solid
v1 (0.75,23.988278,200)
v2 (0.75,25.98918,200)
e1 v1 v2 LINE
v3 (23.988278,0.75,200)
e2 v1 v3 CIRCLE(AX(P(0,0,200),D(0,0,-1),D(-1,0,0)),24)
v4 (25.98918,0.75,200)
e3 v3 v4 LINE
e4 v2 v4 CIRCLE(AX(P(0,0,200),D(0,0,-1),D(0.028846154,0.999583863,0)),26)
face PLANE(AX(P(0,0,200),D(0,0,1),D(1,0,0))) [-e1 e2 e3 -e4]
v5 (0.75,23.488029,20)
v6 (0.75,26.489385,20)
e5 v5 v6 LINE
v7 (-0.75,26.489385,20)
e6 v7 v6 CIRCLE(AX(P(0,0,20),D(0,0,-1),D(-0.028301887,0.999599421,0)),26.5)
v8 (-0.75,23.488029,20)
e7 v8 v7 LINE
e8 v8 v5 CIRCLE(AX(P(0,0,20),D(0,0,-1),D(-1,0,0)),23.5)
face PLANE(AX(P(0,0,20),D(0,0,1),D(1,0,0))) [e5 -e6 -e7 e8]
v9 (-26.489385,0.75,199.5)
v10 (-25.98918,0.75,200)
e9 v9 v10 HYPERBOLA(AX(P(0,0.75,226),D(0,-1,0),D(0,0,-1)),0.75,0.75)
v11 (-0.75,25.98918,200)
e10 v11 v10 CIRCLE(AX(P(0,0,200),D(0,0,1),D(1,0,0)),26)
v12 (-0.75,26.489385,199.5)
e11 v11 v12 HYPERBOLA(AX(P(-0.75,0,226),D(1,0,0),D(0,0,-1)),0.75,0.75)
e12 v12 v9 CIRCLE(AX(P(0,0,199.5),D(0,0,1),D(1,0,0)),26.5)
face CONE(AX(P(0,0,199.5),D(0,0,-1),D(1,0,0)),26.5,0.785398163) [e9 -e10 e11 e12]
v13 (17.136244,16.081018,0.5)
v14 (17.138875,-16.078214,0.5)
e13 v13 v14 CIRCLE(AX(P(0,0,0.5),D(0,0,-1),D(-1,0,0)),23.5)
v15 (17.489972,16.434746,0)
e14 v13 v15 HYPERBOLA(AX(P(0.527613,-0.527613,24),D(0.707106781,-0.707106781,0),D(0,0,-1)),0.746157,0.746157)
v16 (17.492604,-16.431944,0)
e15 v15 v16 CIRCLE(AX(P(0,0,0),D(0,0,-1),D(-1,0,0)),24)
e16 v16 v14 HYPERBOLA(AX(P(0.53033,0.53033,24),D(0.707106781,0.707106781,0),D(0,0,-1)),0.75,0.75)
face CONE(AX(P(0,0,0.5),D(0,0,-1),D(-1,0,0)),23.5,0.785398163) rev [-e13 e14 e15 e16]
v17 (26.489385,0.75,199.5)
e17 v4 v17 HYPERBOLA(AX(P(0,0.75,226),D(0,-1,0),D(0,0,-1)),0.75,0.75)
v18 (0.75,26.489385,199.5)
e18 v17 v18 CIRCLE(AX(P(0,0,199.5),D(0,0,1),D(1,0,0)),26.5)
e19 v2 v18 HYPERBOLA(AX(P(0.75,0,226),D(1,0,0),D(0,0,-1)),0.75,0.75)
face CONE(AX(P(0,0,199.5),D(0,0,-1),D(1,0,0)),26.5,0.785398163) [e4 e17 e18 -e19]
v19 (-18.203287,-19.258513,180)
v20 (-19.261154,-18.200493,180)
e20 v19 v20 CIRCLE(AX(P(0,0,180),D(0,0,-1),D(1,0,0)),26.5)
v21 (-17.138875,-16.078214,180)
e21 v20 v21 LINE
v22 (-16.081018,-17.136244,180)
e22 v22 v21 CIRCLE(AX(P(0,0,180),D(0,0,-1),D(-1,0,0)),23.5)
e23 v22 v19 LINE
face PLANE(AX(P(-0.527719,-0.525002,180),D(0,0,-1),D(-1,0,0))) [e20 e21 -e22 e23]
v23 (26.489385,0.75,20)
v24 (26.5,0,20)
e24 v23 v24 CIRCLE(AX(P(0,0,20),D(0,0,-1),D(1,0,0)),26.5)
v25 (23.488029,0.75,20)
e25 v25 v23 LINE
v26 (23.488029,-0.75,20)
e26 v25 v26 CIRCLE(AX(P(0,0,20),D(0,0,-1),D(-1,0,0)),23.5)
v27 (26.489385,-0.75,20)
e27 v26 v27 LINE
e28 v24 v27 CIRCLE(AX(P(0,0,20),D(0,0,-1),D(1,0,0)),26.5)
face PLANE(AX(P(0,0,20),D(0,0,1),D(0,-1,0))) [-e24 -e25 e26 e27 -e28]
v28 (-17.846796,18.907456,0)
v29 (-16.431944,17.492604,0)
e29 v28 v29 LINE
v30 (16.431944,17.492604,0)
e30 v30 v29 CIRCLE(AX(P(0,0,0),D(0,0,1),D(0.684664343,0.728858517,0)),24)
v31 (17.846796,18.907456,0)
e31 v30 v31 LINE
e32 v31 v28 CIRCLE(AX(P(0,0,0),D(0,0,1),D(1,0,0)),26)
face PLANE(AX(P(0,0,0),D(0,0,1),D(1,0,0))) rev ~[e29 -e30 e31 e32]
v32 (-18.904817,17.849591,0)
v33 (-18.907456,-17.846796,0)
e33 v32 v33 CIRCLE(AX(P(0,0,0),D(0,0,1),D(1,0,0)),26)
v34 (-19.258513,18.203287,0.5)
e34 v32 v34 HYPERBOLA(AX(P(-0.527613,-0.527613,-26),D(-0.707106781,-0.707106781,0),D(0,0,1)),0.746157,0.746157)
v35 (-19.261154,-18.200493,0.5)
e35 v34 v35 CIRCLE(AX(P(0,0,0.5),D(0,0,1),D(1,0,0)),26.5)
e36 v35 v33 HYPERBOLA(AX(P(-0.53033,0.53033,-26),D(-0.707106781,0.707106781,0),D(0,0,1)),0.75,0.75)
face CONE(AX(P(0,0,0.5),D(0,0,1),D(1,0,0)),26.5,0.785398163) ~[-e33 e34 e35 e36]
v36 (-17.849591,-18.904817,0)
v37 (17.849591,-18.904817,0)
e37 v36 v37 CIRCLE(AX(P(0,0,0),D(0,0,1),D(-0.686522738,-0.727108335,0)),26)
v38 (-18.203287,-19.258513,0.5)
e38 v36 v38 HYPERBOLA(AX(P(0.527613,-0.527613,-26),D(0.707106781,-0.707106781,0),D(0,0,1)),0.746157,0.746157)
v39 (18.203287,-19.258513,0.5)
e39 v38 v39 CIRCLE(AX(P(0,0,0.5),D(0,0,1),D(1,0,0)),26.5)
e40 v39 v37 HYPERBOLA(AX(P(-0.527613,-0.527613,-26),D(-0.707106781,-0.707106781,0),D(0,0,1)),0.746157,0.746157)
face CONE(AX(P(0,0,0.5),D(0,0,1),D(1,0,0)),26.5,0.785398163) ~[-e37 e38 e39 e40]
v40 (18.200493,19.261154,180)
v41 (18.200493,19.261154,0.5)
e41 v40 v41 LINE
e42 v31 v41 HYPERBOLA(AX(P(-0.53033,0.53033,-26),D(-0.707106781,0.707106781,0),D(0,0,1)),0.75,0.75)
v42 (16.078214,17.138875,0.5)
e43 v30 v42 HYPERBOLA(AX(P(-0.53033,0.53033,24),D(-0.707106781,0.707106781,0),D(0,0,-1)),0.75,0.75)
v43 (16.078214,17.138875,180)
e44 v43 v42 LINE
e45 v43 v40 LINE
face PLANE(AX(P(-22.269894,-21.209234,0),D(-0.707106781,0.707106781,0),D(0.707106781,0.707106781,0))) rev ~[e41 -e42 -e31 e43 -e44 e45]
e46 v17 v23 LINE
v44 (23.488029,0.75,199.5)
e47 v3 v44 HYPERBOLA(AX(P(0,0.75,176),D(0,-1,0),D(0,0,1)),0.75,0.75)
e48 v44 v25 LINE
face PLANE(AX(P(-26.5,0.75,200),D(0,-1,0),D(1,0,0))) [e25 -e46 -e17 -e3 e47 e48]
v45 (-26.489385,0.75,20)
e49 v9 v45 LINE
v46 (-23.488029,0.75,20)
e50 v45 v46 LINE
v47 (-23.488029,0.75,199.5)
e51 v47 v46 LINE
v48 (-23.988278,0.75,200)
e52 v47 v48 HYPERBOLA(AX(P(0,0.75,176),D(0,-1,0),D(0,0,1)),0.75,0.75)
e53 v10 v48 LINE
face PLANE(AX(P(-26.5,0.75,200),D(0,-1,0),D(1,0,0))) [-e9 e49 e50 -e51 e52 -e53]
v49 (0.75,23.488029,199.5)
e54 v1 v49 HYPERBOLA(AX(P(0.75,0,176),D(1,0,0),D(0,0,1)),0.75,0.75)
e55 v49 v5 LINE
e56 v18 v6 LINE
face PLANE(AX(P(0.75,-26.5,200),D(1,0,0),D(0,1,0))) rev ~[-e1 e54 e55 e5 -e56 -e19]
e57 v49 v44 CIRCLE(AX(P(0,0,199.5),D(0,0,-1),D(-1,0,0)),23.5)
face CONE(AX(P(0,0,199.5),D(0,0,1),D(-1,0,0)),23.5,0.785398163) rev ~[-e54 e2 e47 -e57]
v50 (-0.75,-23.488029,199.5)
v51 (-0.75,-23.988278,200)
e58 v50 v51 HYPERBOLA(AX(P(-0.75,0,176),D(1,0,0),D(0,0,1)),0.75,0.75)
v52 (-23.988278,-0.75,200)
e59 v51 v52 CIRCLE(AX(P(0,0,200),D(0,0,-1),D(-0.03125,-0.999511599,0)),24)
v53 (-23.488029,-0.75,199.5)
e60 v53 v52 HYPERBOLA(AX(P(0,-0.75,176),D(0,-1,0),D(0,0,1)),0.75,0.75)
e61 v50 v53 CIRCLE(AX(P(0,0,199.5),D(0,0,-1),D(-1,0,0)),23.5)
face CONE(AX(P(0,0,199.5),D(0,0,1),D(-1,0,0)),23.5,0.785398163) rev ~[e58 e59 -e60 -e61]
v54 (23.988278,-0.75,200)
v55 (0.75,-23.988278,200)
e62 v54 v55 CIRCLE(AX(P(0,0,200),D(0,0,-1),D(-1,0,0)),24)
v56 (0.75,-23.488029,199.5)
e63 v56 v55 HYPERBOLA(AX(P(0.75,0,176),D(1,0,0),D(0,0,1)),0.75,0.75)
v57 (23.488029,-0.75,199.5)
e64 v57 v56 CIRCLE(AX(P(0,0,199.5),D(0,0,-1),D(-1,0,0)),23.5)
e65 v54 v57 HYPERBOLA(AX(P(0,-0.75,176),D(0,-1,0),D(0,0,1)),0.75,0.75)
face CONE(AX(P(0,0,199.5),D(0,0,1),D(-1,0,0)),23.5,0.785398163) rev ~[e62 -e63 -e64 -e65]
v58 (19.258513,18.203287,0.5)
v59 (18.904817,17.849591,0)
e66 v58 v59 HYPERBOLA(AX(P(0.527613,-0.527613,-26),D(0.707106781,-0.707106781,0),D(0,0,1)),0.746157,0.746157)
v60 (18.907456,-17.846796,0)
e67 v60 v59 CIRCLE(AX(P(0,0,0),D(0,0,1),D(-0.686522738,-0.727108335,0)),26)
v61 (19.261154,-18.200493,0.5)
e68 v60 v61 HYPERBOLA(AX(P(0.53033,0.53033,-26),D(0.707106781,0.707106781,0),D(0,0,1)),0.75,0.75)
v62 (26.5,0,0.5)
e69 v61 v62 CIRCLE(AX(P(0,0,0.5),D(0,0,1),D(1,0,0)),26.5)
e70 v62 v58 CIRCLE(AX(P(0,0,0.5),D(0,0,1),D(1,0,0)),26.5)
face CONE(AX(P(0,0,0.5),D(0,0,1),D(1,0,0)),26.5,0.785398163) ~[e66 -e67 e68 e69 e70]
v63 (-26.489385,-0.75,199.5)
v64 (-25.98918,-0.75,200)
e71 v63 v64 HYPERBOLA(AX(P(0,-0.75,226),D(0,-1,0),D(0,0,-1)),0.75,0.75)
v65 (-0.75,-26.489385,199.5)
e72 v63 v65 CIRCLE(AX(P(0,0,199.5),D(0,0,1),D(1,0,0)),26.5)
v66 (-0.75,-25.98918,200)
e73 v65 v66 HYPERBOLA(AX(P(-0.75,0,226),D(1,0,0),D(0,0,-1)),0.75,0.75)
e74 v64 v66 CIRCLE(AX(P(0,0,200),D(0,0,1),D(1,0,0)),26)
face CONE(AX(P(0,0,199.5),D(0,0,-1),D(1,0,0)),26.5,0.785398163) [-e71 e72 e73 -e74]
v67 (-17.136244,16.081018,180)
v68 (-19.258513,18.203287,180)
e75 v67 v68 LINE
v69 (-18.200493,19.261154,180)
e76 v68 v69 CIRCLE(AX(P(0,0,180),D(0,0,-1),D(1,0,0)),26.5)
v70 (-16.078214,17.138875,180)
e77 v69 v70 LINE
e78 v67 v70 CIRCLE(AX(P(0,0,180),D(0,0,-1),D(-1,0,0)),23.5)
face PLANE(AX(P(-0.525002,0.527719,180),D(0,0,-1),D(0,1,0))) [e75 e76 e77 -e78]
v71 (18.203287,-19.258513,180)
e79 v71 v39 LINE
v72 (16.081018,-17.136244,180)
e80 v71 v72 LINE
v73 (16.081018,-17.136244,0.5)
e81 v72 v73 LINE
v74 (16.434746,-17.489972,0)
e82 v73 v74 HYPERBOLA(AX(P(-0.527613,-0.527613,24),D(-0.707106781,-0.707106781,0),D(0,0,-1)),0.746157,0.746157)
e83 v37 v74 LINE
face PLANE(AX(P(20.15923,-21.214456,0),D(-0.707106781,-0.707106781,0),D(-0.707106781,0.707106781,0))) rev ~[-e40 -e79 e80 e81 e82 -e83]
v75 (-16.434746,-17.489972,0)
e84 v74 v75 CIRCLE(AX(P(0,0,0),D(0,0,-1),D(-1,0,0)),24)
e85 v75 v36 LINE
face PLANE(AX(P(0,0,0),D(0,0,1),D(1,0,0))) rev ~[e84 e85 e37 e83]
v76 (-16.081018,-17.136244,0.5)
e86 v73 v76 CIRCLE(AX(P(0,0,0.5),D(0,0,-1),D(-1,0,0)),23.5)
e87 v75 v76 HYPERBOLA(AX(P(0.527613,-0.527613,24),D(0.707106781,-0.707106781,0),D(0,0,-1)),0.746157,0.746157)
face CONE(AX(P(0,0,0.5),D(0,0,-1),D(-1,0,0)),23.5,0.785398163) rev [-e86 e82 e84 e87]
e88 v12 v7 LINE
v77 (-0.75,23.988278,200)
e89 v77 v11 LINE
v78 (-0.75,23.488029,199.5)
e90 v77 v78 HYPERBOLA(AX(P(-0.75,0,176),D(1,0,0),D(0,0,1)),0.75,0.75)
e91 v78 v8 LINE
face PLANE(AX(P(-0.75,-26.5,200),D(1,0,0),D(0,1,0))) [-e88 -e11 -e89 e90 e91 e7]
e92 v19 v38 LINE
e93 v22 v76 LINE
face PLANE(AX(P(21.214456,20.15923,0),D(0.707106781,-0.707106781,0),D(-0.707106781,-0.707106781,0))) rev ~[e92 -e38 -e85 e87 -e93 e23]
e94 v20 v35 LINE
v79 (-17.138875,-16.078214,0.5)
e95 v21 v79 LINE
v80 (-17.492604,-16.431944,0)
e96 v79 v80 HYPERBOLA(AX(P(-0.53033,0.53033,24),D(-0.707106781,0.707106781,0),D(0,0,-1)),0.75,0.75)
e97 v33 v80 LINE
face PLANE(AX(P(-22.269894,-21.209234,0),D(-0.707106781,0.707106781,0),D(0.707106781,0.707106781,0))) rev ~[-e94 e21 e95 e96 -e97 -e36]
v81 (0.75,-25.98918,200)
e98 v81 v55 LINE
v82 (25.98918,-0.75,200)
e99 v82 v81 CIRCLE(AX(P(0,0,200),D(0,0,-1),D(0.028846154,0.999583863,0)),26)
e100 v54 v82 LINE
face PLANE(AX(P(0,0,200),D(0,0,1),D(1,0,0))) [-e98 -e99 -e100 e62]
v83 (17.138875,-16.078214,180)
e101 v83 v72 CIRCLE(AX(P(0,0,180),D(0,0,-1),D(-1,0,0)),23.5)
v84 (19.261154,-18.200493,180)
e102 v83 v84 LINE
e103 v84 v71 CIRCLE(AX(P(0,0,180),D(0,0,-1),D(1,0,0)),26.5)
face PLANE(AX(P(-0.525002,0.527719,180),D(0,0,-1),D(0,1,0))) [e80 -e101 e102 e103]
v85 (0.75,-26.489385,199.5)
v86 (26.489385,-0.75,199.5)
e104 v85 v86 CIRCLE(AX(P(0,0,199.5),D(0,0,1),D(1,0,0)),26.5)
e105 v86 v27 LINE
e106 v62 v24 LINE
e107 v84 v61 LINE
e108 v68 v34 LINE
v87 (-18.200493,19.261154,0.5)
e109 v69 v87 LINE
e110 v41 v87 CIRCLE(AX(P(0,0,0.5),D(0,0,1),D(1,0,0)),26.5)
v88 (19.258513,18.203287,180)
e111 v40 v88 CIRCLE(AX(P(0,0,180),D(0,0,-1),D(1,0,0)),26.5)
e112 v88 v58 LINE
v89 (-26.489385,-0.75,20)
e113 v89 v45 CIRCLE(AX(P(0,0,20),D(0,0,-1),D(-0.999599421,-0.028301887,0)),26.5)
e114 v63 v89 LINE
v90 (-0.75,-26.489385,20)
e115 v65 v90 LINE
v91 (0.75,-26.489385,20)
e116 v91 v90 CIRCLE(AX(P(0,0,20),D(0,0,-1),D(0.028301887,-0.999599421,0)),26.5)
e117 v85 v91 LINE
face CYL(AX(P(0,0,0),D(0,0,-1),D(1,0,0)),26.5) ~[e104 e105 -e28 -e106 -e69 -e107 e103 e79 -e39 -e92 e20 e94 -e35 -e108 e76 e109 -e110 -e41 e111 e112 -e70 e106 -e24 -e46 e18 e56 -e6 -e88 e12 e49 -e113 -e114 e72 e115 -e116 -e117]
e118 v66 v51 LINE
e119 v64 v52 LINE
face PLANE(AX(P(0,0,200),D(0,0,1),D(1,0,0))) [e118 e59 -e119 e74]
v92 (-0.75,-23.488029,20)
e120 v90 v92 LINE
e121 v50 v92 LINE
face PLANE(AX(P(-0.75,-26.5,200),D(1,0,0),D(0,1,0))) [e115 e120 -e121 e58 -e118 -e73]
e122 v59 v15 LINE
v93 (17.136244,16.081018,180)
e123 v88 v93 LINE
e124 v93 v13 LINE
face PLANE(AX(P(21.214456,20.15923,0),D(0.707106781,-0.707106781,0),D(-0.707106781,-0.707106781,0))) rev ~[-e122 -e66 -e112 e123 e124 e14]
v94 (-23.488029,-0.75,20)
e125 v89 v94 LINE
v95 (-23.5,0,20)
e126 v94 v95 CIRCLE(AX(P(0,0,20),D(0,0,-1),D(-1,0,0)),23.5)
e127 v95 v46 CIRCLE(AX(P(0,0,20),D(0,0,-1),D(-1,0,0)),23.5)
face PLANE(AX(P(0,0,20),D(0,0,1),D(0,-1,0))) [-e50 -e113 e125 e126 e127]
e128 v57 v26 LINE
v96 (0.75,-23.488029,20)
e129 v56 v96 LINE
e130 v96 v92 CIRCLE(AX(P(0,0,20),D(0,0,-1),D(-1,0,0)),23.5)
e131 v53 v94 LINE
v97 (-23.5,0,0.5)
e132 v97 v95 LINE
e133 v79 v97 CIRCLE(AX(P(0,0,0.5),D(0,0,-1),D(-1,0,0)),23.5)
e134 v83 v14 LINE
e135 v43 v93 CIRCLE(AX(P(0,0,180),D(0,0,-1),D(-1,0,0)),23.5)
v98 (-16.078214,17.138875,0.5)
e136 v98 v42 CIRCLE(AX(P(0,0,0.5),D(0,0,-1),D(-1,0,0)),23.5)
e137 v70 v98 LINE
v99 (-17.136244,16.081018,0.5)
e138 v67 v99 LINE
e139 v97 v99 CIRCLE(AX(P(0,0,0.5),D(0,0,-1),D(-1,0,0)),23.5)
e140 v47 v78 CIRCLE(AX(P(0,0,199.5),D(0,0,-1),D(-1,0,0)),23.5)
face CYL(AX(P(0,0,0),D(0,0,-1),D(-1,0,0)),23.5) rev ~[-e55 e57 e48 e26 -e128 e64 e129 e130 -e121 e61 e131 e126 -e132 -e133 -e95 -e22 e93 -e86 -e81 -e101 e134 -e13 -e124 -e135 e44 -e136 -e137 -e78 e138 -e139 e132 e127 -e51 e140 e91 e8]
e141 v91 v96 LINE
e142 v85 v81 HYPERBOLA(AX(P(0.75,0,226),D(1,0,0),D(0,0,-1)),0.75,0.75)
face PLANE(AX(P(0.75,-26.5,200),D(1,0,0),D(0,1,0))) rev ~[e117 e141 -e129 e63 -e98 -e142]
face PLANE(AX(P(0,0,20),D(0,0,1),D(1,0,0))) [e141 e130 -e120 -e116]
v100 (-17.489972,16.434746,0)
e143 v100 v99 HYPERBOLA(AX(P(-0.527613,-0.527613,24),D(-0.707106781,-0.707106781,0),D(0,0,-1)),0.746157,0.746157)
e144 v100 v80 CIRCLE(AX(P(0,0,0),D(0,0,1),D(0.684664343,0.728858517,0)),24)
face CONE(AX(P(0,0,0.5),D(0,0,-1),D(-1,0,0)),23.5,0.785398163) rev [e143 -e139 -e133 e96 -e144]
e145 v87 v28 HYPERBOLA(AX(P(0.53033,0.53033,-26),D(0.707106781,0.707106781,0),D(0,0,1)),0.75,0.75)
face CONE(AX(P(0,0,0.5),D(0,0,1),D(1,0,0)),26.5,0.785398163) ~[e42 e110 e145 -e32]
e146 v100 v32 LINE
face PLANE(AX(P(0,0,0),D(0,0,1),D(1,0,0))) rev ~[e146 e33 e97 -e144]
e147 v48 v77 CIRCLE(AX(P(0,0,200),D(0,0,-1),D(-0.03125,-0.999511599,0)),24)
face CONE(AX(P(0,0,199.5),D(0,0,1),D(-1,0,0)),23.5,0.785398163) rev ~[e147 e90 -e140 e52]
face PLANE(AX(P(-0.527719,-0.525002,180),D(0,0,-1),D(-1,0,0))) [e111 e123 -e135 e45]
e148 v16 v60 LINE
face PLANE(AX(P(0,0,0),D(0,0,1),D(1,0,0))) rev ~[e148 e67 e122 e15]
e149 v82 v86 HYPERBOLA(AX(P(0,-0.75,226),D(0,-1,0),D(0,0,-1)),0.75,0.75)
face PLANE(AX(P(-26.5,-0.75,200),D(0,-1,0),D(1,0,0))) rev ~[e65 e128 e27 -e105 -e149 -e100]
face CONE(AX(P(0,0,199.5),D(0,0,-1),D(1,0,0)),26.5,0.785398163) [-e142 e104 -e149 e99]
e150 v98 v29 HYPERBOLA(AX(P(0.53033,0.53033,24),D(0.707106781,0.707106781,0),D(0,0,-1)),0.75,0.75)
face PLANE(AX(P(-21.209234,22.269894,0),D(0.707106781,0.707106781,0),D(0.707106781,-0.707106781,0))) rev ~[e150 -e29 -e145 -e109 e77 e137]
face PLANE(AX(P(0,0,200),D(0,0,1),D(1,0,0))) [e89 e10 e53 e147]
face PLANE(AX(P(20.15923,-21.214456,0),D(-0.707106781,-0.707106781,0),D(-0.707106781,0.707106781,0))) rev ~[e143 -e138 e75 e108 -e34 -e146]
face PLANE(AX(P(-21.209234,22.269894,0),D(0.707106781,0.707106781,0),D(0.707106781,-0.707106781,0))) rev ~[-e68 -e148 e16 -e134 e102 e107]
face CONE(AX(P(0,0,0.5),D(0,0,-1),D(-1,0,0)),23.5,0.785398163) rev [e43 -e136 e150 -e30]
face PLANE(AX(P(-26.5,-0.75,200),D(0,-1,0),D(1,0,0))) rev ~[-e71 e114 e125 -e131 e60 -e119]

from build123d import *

# Parameters (mm, degrees)
SKETCH1_R           = 26.5
BOSS_EXTRUDE1_DEPTH = 200
SKETCH2_R           = 23.5
CUT_EXTRUDE1_DEPTH  = 200
CHAMFER1_SIZE       = 0.5
SKETCH4_W           = 1.5
SKETCH4_H           = 53
CUT_EXTRUDE2_DEPTH  = 180
CIRPATTERN1_COUNT   = 2
CIRPATTERN1_ANGLE   = 90
CUT_EXTRUDE3_DEPTH  = 180
CIRPATTERN2_COUNT   = 2
CIRPATTERN2_ANGLE   = 90


with BuildPart() as part:
    # Sketch1 → Boss-Extrude1 (new body)
    with BuildSketch(Plane.XY):
        Circle(SKETCH1_R)
    extrude(amount=BOSS_EXTRUDE1_DEPTH)

    # Sketch2 → Cut-Extrude1 (cut)
    with BuildSketch(Plane(origin=(0, 0, 0), x_dir=(-1, 0, 0), z_dir=(0, 0, -1))):
        Circle(SKETCH2_R)
    extrude(amount=-CUT_EXTRUDE1_DEPTH, mode=Mode.SUBTRACT)

    # Chamfer1
    chamfer1_edges = [part.edges().sort_by_distance(p)[0] for p in [
        (-26.5, 0, 0),
        (-26.5, 0, 200),
        (23.5, 0, 200),
        (23.5, 0, 0),
    ]]
    chamfer(chamfer1_edges, length=CHAMFER1_SIZE)

    # Sketch4 → Cut-Extrude2 (cut)
    with BuildSketch(Plane.XY.offset(200)):
        Rectangle(SKETCH4_W, SKETCH4_H)
    cut_extrude2 = extrude(amount=-CUT_EXTRUDE2_DEPTH, mode=Mode.SUBTRACT)

    # CirPattern1: Cut-Extrude2 ×2 about axis
    cirpattern1_axis = Axis((0, 0, 199.5), (0, 0, -1))
    for i in range(1, CIRPATTERN1_COUNT):
        add(cut_extrude2.rotate(cirpattern1_axis, i * CIRPATTERN1_ANGLE / (CIRPATTERN1_COUNT - 1)), mode=Mode.SUBTRACT)

    # Sketch5 → Cut-Extrude3 (cut)
    with BuildSketch(Plane(origin=(0, 0, 0), x_dir=(-1, 0, 0), z_dir=(0, 0, -1))):
        Polygon((-21.214455758, 20.159230222), (21.211951113, -22.267176649), (22.269893967, -21.209233795), (-20.156512904, 21.217173076), align=None)
    cut_extrude3 = extrude(amount=-CUT_EXTRUDE3_DEPTH, mode=Mode.SUBTRACT)

    # CirPattern2: Cut-Extrude3 ×2 about axis
    cirpattern2_axis = Axis((0, 0, 199.5), (0, 0, -1))
    for i in range(1, CIRPATTERN2_COUNT):
        add(cut_extrude3.rotate(cirpattern2_axis, i * CIRPATTERN2_ANGLE / (CIRPATTERN2_COUNT - 1)), mode=Mode.SUBTRACT)


solid = part.part
